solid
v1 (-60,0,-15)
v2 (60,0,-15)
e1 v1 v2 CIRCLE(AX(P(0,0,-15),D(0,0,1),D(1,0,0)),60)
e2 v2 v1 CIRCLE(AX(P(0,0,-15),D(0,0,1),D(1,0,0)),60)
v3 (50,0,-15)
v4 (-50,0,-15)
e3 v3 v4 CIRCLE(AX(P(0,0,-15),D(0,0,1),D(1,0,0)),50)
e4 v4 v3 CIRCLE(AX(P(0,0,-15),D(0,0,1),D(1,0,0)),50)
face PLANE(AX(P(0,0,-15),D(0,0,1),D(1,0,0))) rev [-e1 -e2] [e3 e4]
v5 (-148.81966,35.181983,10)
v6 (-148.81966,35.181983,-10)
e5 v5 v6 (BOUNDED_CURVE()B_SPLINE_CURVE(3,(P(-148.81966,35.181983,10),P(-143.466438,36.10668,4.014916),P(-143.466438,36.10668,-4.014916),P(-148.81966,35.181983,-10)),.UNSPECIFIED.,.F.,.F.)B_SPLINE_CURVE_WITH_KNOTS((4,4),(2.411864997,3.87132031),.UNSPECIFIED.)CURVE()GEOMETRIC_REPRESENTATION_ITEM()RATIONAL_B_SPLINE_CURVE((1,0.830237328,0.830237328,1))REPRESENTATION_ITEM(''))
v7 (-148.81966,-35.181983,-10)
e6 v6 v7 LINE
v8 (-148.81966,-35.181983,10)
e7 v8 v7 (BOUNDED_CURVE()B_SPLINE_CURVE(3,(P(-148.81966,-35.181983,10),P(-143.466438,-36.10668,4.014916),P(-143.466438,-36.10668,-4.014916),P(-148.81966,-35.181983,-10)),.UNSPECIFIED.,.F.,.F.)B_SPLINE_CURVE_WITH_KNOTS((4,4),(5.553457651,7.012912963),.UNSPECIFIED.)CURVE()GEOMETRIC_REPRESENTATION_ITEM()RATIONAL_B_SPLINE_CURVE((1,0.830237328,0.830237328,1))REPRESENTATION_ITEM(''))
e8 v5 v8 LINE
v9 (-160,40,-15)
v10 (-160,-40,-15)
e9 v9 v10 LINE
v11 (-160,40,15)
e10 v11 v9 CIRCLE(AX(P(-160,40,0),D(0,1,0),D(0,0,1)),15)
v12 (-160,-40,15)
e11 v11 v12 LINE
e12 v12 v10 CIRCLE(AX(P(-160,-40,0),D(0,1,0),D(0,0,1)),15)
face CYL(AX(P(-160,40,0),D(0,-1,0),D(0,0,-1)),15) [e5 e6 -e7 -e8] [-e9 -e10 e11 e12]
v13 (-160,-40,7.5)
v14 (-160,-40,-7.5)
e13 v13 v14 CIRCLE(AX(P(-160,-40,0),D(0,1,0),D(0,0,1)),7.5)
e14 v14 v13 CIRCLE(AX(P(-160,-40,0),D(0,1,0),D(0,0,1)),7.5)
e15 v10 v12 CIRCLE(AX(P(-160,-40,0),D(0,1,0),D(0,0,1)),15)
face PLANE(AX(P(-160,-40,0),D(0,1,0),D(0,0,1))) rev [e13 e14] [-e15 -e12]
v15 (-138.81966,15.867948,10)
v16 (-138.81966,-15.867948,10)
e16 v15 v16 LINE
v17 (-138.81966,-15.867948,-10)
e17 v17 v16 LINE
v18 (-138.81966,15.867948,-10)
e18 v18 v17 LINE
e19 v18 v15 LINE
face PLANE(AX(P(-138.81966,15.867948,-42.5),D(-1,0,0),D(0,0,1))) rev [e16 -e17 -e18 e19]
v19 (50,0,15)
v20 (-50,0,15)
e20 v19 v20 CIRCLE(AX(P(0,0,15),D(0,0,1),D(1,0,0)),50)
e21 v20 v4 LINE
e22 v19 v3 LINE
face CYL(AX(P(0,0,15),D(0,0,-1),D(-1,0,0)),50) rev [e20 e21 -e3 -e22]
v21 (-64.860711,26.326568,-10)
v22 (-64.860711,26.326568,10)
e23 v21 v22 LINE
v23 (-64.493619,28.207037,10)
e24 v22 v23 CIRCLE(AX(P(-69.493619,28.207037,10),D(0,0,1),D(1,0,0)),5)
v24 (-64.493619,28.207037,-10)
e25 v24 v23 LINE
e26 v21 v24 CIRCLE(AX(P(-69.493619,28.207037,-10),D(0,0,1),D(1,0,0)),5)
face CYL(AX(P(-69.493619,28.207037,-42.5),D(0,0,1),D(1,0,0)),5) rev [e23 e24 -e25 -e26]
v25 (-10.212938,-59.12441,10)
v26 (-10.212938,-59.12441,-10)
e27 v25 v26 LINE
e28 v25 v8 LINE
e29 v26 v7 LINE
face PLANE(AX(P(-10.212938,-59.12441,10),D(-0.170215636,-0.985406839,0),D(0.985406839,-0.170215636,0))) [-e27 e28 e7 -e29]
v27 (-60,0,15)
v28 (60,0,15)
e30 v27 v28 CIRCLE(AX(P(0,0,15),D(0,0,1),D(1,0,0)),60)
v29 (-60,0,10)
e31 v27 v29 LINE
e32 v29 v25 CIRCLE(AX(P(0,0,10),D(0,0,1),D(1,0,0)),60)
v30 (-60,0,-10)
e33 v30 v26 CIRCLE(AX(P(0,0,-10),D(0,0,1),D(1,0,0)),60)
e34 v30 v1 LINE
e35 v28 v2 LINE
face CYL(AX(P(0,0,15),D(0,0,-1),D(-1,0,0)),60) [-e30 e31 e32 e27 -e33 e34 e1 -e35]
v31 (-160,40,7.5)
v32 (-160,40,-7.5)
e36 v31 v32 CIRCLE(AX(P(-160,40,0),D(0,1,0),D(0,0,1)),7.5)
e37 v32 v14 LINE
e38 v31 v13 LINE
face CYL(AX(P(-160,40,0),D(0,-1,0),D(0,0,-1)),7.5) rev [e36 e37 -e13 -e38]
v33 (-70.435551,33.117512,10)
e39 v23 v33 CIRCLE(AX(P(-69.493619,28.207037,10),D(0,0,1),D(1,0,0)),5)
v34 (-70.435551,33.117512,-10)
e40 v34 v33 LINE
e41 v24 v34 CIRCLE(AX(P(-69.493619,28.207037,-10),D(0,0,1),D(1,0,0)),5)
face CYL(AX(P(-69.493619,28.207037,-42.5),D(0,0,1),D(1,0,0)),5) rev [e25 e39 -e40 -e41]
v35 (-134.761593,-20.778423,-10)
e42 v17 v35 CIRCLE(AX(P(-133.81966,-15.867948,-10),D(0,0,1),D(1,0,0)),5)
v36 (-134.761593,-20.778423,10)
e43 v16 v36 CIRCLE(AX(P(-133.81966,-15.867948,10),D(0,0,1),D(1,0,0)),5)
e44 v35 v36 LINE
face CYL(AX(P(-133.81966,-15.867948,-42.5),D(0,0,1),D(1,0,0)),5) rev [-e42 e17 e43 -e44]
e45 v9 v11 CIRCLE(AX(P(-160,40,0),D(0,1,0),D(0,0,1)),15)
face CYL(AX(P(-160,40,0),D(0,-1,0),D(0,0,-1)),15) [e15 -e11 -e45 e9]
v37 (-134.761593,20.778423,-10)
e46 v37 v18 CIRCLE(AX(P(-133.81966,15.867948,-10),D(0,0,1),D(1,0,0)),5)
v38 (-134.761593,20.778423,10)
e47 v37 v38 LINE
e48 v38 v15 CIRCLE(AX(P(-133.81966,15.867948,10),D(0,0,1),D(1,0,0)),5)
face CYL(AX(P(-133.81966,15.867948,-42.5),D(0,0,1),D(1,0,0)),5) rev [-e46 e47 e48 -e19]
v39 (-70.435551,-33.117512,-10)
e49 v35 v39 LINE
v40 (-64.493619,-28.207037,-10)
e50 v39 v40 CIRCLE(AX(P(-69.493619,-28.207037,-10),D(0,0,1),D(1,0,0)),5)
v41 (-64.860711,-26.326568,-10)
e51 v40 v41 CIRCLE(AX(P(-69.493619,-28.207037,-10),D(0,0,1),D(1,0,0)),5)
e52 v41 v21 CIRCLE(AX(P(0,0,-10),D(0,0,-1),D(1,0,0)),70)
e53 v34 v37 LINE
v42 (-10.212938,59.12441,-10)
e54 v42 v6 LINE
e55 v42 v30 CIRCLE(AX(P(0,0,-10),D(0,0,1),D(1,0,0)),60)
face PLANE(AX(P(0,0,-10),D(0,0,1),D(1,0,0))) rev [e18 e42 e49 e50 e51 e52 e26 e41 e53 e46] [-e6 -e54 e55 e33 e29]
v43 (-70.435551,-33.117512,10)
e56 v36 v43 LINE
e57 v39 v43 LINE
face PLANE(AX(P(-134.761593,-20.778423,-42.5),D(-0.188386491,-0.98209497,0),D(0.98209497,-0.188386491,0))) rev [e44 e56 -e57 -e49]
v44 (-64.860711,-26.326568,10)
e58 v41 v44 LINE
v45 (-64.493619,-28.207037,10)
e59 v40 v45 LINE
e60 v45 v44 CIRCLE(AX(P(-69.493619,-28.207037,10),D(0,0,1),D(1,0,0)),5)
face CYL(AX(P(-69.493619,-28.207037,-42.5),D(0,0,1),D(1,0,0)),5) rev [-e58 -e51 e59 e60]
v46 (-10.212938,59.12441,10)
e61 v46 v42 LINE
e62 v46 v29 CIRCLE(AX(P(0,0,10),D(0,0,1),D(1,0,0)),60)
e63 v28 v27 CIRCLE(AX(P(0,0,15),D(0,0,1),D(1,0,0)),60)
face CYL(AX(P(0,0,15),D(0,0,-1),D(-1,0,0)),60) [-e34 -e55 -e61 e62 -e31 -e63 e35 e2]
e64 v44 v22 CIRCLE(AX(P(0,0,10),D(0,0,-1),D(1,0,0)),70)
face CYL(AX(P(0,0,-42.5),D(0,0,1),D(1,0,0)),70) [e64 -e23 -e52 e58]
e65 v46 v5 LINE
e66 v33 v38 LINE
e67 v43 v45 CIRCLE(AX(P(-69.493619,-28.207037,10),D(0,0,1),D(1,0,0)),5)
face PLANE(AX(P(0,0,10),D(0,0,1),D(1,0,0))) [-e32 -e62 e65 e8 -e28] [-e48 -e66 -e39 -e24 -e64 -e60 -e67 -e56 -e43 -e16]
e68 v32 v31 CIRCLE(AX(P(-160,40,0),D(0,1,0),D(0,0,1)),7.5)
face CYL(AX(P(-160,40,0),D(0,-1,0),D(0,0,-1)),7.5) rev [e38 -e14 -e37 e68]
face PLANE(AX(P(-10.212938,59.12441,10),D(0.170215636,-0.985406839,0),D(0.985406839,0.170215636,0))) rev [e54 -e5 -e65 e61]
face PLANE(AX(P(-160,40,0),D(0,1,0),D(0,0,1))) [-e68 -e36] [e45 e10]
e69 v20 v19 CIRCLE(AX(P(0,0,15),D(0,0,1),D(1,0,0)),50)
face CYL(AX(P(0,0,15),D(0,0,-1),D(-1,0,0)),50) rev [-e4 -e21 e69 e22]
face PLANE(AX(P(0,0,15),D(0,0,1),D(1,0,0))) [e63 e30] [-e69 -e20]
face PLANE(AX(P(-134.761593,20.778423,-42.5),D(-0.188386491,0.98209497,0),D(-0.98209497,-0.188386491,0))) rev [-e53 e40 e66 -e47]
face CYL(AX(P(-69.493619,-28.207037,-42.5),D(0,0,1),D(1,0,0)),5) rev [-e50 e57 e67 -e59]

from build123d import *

# Parameters (mm, degrees)
BIG_END_RING_SKETCH_R       = 60
BIG_END_RING_SKETCH_R_2     = 50
BIG_END_RING_120_DEPTH      = 15
SMALL_END_BOSS_SKETCH_R     = 15
SMALL_END_BOSS_SKETCH_R_2   = 7.5
SMALL_END_BOSS_30_DEPTH     = 40
CONNECTING_WEB_DEPTH        = 10
WEB_LIGHTENING_WINDOW_DEPTH = 52.5


with BuildPart() as part:
    # Big End Ring Sketch → Big End Ring Ø120 (new, symmetric)
    with BuildSketch(Plane.XY):
        Circle(BIG_END_RING_SKETCH_R)
        Circle(BIG_END_RING_SKETCH_R_2, mode=Mode.SUBTRACT)
    extrude(amount=BIG_END_RING_120_DEPTH, both=True)



with BuildPart() as body_2:
    # Small End Boss Sketch → Small End Boss Ø30 (new, symmetric)
    with BuildSketch(Plane(origin=(0, 0, 0), x_dir=(1, 0, 0), z_dir=(0, 1, 0))):
        with Locations(Location((-160, 0, 0), (0, 0, 270))):
            Circle(SMALL_END_BOSS_SKETCH_R)
        with Locations(Location((-160, 0, 0), (0, 0, 270))):
            Circle(SMALL_END_BOSS_SKETCH_R_2, mode=Mode.SUBTRACT)
    extrude(amount=SMALL_END_BOSS_30_DEPTH, both=True)


with BuildPart() as part_1:
    add(part.part)

    add(body_2.part)  # Connecting Web merges body 2
    # Web Profile Sketch → Connecting Web (add, symmetric)
    with BuildSketch(Plane.XY):
        with BuildLine():
            Line((-10.212938139, 59.12441031), (-149.873192049, 35))
            Line((-149.873192049, 35), (-149.873192049, -35))
            Line((-149.873192049, -35), (-10.212938139, -59.12441031))
            ThreePointArc((-10.212938139, -59.12441031), (-60, 0), (-10.212938139, 59.12441031))
        make_face()
    extrude(amount=CONNECTING_WEB_DEPTH, both=True)

    # Web Window Sketch → Web Lightening Window (cut, symmetric)
    with BuildSketch(Plane.XY.offset(10)):
        with BuildLine():
            Line((-138.819660113, 15.867947938), (-138.819660113, -15.867947938))
            ThreePointArc((-138.819660113, -15.867947938), (-137.673856674, -19.053096108), (-134.761592567, -20.778422788))
            Line((-134.761592567, -20.778422788), (-70.43555138, -33.117511712))
            ThreePointArc((-70.43555138, -33.117511712), (-65.629029038, -31.379566609), (-64.860710998, -26.326567738))
            ThreePointArc((-64.860710998, -26.326567738), (-70, 0), (-64.860710998, 26.326567738))
            ThreePointArc((-64.860710998, 26.326567738), (-65.629029038, 31.379566609), (-70.43555138, 33.117511712))
            Line((-70.43555138, 33.117511712), (-134.761592567, 20.778422788))
            ThreePointArc((-134.761592567, 20.778422788), (-137.673856674, 19.053096108), (-138.819660113, 15.867947938))
        make_face()
    extrude(amount=WEB_LIGHTENING_WINDOW_DEPTH, both=True, mode=Mode.SUBTRACT)


solid = part_1.part
